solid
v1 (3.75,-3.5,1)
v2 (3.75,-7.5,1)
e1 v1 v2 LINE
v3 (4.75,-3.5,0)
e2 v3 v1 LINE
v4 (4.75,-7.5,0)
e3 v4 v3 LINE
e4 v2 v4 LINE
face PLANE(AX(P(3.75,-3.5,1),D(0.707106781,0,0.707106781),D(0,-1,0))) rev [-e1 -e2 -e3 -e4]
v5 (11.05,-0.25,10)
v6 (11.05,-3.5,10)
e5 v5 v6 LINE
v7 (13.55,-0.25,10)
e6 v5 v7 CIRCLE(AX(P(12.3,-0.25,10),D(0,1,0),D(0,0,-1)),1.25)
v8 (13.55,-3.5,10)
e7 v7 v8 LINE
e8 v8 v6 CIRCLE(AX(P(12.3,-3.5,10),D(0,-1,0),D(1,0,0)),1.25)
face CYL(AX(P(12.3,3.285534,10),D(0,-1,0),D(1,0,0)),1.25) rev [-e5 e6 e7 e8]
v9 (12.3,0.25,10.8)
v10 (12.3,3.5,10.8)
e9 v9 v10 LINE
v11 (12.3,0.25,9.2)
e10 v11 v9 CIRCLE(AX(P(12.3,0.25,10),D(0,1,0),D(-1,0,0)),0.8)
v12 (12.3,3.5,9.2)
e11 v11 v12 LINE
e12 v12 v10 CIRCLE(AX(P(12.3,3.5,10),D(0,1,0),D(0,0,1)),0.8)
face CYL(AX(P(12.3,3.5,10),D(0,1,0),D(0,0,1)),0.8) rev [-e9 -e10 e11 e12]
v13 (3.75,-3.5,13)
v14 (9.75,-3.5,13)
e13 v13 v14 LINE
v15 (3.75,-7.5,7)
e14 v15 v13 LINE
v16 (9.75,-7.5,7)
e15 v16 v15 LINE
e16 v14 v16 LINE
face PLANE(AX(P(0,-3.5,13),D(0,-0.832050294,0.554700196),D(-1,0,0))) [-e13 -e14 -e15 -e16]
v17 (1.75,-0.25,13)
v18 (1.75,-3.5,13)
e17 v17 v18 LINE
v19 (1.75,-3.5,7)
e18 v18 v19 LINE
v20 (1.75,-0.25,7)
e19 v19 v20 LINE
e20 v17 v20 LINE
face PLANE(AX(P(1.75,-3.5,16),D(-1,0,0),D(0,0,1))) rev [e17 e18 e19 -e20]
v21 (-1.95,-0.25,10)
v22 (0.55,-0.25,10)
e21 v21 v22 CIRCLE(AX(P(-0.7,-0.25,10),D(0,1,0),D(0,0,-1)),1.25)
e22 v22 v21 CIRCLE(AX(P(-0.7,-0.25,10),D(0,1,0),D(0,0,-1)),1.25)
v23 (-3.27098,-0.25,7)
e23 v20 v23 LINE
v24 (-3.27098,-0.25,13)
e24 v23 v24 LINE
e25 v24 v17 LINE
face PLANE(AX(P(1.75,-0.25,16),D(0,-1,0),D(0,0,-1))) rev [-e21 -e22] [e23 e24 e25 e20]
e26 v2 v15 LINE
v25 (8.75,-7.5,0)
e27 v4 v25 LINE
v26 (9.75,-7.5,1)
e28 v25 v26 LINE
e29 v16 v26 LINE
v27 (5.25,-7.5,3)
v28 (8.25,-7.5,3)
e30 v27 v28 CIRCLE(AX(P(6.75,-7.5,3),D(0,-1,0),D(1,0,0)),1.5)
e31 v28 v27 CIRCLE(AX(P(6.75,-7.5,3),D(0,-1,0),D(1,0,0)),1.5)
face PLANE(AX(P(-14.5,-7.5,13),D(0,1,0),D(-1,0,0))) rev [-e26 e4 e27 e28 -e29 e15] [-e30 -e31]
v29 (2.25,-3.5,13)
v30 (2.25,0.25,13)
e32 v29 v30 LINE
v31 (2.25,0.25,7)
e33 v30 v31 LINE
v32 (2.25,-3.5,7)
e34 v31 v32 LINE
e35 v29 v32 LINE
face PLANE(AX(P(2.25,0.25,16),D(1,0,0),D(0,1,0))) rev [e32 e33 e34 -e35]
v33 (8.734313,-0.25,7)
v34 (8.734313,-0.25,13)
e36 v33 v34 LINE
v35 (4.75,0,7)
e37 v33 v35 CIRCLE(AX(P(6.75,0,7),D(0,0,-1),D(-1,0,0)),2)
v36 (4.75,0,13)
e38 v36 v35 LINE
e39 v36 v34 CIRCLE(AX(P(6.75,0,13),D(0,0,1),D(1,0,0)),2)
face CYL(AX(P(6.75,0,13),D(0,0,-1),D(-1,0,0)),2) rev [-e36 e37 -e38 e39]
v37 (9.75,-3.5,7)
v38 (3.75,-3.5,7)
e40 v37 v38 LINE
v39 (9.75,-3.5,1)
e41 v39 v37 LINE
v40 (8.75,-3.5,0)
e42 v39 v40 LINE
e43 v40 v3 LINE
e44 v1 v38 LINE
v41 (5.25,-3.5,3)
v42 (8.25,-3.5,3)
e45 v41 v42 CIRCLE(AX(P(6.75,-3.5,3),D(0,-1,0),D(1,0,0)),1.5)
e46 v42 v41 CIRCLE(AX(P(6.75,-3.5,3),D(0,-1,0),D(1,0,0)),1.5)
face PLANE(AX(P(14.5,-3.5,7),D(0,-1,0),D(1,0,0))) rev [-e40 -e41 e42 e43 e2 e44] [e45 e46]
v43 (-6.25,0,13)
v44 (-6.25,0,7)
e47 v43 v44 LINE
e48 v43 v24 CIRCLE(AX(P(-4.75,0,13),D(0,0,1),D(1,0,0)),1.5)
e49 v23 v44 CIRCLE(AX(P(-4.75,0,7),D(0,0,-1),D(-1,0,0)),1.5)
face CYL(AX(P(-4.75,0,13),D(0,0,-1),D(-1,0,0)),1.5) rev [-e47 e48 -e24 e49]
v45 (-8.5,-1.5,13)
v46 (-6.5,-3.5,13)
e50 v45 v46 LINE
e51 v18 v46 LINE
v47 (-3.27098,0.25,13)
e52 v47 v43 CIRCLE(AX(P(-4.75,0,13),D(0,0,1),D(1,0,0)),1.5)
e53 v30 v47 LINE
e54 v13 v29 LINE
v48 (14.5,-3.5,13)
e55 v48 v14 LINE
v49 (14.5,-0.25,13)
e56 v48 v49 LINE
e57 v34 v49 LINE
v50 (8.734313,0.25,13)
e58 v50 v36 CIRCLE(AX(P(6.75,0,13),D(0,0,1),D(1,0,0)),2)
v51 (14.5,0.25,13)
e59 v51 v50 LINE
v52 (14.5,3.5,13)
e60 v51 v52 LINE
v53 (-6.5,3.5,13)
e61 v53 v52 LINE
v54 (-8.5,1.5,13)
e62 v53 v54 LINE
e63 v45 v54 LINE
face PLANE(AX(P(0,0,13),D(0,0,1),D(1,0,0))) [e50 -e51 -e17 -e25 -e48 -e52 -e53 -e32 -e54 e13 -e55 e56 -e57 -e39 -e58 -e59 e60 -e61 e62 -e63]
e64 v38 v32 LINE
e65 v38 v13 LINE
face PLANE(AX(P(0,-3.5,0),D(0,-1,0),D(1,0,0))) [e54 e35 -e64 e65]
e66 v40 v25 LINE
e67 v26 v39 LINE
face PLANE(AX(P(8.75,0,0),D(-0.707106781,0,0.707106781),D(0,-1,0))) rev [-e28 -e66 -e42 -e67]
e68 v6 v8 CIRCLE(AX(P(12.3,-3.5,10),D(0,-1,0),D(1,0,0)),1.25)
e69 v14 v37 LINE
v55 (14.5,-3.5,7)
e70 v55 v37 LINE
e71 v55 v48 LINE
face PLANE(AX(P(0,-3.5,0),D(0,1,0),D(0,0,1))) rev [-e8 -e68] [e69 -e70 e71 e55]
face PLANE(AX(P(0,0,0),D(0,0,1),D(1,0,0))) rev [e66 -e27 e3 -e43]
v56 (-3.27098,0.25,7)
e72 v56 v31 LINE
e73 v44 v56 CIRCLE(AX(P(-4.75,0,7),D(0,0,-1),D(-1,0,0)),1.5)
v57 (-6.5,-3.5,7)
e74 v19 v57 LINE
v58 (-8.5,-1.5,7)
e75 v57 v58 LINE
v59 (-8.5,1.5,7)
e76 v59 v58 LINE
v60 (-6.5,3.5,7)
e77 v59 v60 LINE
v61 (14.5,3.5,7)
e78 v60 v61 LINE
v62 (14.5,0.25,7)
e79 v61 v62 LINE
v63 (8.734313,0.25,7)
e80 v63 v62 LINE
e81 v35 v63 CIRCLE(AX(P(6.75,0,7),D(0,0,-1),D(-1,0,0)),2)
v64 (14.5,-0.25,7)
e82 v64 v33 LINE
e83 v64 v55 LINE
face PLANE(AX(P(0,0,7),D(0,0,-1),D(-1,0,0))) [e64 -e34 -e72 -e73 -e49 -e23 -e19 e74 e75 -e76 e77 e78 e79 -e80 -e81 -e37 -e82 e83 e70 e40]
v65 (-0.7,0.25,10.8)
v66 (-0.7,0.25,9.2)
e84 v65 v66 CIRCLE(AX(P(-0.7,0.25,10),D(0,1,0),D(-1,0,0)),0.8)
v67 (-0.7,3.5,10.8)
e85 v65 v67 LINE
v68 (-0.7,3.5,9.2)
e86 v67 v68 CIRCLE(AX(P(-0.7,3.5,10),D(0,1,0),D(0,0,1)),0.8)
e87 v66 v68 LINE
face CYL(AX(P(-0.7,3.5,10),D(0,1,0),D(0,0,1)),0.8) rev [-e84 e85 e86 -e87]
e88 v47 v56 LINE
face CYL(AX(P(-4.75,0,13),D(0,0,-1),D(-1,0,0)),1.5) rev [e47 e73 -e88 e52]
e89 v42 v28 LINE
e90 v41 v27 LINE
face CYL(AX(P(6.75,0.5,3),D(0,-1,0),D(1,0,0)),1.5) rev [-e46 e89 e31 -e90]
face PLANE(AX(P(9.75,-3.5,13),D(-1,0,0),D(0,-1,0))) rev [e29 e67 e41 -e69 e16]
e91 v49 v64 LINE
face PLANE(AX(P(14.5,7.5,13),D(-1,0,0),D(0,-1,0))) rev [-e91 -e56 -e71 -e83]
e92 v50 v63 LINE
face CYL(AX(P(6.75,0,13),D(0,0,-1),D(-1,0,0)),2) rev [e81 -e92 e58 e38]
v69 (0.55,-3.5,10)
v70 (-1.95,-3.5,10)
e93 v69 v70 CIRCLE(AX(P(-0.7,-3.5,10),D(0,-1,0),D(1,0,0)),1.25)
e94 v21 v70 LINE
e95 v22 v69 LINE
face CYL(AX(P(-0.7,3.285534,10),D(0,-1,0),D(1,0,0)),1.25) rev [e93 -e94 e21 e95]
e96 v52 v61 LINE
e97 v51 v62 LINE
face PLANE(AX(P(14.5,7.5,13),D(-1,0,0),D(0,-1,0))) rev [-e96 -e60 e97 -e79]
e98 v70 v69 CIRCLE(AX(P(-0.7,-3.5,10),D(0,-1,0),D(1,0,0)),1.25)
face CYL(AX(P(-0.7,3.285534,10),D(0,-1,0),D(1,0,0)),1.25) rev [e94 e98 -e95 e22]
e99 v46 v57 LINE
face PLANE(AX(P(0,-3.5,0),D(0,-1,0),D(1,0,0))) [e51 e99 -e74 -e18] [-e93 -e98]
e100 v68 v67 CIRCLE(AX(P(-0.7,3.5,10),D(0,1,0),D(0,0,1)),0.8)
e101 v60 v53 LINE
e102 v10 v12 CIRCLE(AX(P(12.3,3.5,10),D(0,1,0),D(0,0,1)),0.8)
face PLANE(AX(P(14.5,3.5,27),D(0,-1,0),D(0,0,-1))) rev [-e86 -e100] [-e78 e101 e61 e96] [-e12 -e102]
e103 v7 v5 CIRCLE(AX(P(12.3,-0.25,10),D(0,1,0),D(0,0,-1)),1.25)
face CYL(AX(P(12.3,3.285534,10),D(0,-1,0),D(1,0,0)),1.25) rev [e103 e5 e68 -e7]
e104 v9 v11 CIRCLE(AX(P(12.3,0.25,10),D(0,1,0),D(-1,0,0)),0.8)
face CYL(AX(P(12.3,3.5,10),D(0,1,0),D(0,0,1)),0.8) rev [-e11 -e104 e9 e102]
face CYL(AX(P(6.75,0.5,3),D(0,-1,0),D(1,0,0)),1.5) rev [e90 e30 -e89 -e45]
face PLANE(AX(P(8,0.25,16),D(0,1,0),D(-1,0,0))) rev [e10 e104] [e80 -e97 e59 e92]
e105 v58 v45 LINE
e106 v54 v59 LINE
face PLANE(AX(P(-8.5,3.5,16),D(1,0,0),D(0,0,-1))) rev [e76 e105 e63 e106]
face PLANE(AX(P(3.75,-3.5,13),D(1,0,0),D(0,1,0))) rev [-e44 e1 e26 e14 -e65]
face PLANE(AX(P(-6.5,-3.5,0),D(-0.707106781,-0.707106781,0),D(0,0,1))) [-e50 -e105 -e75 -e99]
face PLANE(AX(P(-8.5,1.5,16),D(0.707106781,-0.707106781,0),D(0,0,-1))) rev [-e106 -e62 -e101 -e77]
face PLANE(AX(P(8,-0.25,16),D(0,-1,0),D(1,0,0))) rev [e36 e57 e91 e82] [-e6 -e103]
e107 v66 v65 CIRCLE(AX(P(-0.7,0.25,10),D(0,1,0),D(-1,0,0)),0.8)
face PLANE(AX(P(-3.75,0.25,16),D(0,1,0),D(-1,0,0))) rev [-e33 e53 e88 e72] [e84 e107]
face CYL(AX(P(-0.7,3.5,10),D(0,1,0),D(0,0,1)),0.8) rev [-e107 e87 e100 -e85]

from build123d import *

# Parameters (mm, degrees)
SKETCH1_W           = 29
SKETCH1_H           = 15
SKETCH1_R           = 2
SKETCH1_R_2         = 1.5
BOSS_EXTRUDE1_DEPTH = 13
SKETCH3_W           = 4.75
SKETCH3_H           = 13
SKETCH3_W_2         = 18.25
CUT_EXTRUDE1_DEPTH  = 4
SKETCH5_W           = 29
SKETCH5_H           = 4
CUT_EXTRUDE2_DEPTH  = 27
SKETCH6_W           = 1.5
SKETCH6_H           = 7
CUT_EXTRUDE3_DEPTH  = 27
SKETCH7_W           = 27.5
SKETCH7_H           = 7
CUT_EXTRUDE4_DEPTH  = 7
CHAMFER1_SIZE       = 6
CHAMFER1_SIZE2      = 4
SKETCH8_W           = 6.5
SKETCH8_H           = 0.5
CUT_EXTRUDE5_DEPTH  = 9
SKETCH9_R           = 1.25
CUT_EXTRUDE6_DEPTH  = 3.25
SKETCH12_W          = 3
SKETCH12_H          = 7
CUT_EXTRUDE8_DEPTH  = 8
SKETCH13_R          = 1.5
CUT_EXTRUDE9_DEPTH  = 8
CHAMFER3_SIZE       = 1
SKETCH17_W          = 1.5
SKETCH17_H          = 7
CUT_EXTRUDE11_DEPTH = 9
CHAMFER4_SIZE       = 2
M2_TAPPED_HOLE1_D   = 1.6


with BuildPart() as part:
    # Sketch1 → Boss-Extrude1 (new body)
    with BuildSketch(Plane.XY):
        Rectangle(SKETCH1_W, SKETCH1_H)
        with Locations(Location((6.75, 0, 0), (0, 0, 180))):
            Circle(SKETCH1_R, mode=Mode.SUBTRACT)
        with Locations(Location((-4.75, 0, 0), (0, 0, 180))):
            Circle(SKETCH1_R_2, mode=Mode.SUBTRACT)
    extrude(amount=BOSS_EXTRUDE1_DEPTH)

    # Sketch3 → Cut-Extrude1 (cut)
    with BuildSketch(Plane.XZ.offset(7.5)):
        with Locations((12.125, 6.5)):
            Rectangle(SKETCH3_W, SKETCH3_H)
        with Locations((-5.375, 6.5)):
            Rectangle(SKETCH3_W_2, SKETCH3_H)
    extrude(amount=-CUT_EXTRUDE1_DEPTH, mode=Mode.SUBTRACT)

    # Sketch5 → Cut-Extrude2 (cut)
    with BuildSketch(Plane(origin=(0, 0, 0), x_dir=(-1, 0, 0), z_dir=(0, 0, -1))):
        with Locations((0, 5.5)):
            Rectangle(SKETCH5_W, SKETCH5_H)
    extrude(amount=-CUT_EXTRUDE2_DEPTH, mode=Mode.SUBTRACT)

    # Sketch6 → Cut-Extrude3 (cut)
    with BuildSketch(Plane(origin=(0, 0, 0), x_dir=(-1, 0, 0), z_dir=(0, 0, -1))):
        with Locations((13.75, 0)):
            Rectangle(SKETCH6_W, SKETCH6_H)
    extrude(amount=-CUT_EXTRUDE3_DEPTH, mode=Mode.SUBTRACT)

    # Sketch7 → Cut-Extrude4 (cut)
    with BuildSketch(Plane(origin=(0, 0, 0), x_dir=(-1, 0, 0), z_dir=(0, 0, -1))):
        with Locations((-0.75, 0)):
            Rectangle(SKETCH7_W, SKETCH7_H)
    extrude(amount=-CUT_EXTRUDE4_DEPTH, mode=Mode.SUBTRACT)

    # Chamfer1
    chamfer1_edges = [part.edges().sort_by_distance(p)[0] for p in [
        (6.75, -7.5, 13),
    ]]
    chamfer1_side = [part.faces().sort_by_distance(p)[0] for p in [
        (6.75, -7.5, 6.5),
    ]]
    chamfer(chamfer1_edges, length=CHAMFER1_SIZE, length2=CHAMFER1_SIZE2, reference=chamfer1_side[0])

    # Sketch8 → Cut-Extrude5 (cut)
    with BuildSketch(Plane(origin=(0, 0, 7), x_dir=(-1, 0, 0), z_dir=(0, 0, -1))):
        Polygon((-1.75, -3.5), (-1.75, -0.25), (3.75, -0.25), (3.75, 0.25), (-2.25, 0.25), (-2.25, -3.5), align=None)
        with Locations((-11.25, 0)):
            Rectangle(SKETCH8_W, SKETCH8_H)
    extrude(amount=-CUT_EXTRUDE5_DEPTH, mode=Mode.SUBTRACT)

    # Sketch9 → Cut-Extrude6 (cut)
    with BuildSketch(Plane.XZ.offset(3.5)):
        with Locations((12.3, 10)):
            Circle(SKETCH9_R)
        with Locations((-0.7, 10)):
            Circle(SKETCH9_R)
    extrude(amount=-CUT_EXTRUDE6_DEPTH, mode=Mode.SUBTRACT)

    # Sketch12 → Cut-Extrude8 (cut)
    with BuildSketch(Plane.XY.offset(13)):
        with Locations((-11.5, 0)):
            Rectangle(SKETCH12_W, SKETCH12_H)
    extrude(amount=-CUT_EXTRUDE8_DEPTH, mode=Mode.SUBTRACT)

    # Sketch13 → Cut-Extrude9 (cut)
    with BuildSketch(Plane.XZ.offset(7.5)):
        with Locations((6.75, 3)):
            Circle(SKETCH13_R)
    extrude(amount=-CUT_EXTRUDE9_DEPTH, mode=Mode.SUBTRACT)

    # Chamfer3
    chamfer3_edges = [part.edges().sort_by_distance(p)[0] for p in [
        (9.75, -5.5, 0),
        (3.75, -5.5, 0),
    ]]
    chamfer(chamfer3_edges, length=CHAMFER3_SIZE)

    # Sketch17 → Cut-Extrude11 (cut)
    with BuildSketch(Plane(origin=(0, 0, 7), x_dir=(-1, 0, 0), z_dir=(0, 0, -1))):
        with Locations((9.25, 0)):
            Rectangle(SKETCH17_W, SKETCH17_H)
    extrude(amount=-CUT_EXTRUDE11_DEPTH, mode=Mode.SUBTRACT)

    # Chamfer4
    chamfer4_edges = [part.edges().sort_by_distance(p)[0] for p in [
        (-8.5, -3.5, 10),
        (-8.5, 3.5, 10),
    ]]
    chamfer(chamfer4_edges, length=CHAMFER4_SIZE)

    # M2 Tapped Hole1 (through all)
    with Locations(Plane(origin=(0, 3.5, 0), x_dir=(1, 0, 0), z_dir=(0, 1, 0))):
        with Locations((-0.7, -10), (12.3, -10)):
            Hole(M2_TAPPED_HOLE1_D / 2)


solid = part.part
